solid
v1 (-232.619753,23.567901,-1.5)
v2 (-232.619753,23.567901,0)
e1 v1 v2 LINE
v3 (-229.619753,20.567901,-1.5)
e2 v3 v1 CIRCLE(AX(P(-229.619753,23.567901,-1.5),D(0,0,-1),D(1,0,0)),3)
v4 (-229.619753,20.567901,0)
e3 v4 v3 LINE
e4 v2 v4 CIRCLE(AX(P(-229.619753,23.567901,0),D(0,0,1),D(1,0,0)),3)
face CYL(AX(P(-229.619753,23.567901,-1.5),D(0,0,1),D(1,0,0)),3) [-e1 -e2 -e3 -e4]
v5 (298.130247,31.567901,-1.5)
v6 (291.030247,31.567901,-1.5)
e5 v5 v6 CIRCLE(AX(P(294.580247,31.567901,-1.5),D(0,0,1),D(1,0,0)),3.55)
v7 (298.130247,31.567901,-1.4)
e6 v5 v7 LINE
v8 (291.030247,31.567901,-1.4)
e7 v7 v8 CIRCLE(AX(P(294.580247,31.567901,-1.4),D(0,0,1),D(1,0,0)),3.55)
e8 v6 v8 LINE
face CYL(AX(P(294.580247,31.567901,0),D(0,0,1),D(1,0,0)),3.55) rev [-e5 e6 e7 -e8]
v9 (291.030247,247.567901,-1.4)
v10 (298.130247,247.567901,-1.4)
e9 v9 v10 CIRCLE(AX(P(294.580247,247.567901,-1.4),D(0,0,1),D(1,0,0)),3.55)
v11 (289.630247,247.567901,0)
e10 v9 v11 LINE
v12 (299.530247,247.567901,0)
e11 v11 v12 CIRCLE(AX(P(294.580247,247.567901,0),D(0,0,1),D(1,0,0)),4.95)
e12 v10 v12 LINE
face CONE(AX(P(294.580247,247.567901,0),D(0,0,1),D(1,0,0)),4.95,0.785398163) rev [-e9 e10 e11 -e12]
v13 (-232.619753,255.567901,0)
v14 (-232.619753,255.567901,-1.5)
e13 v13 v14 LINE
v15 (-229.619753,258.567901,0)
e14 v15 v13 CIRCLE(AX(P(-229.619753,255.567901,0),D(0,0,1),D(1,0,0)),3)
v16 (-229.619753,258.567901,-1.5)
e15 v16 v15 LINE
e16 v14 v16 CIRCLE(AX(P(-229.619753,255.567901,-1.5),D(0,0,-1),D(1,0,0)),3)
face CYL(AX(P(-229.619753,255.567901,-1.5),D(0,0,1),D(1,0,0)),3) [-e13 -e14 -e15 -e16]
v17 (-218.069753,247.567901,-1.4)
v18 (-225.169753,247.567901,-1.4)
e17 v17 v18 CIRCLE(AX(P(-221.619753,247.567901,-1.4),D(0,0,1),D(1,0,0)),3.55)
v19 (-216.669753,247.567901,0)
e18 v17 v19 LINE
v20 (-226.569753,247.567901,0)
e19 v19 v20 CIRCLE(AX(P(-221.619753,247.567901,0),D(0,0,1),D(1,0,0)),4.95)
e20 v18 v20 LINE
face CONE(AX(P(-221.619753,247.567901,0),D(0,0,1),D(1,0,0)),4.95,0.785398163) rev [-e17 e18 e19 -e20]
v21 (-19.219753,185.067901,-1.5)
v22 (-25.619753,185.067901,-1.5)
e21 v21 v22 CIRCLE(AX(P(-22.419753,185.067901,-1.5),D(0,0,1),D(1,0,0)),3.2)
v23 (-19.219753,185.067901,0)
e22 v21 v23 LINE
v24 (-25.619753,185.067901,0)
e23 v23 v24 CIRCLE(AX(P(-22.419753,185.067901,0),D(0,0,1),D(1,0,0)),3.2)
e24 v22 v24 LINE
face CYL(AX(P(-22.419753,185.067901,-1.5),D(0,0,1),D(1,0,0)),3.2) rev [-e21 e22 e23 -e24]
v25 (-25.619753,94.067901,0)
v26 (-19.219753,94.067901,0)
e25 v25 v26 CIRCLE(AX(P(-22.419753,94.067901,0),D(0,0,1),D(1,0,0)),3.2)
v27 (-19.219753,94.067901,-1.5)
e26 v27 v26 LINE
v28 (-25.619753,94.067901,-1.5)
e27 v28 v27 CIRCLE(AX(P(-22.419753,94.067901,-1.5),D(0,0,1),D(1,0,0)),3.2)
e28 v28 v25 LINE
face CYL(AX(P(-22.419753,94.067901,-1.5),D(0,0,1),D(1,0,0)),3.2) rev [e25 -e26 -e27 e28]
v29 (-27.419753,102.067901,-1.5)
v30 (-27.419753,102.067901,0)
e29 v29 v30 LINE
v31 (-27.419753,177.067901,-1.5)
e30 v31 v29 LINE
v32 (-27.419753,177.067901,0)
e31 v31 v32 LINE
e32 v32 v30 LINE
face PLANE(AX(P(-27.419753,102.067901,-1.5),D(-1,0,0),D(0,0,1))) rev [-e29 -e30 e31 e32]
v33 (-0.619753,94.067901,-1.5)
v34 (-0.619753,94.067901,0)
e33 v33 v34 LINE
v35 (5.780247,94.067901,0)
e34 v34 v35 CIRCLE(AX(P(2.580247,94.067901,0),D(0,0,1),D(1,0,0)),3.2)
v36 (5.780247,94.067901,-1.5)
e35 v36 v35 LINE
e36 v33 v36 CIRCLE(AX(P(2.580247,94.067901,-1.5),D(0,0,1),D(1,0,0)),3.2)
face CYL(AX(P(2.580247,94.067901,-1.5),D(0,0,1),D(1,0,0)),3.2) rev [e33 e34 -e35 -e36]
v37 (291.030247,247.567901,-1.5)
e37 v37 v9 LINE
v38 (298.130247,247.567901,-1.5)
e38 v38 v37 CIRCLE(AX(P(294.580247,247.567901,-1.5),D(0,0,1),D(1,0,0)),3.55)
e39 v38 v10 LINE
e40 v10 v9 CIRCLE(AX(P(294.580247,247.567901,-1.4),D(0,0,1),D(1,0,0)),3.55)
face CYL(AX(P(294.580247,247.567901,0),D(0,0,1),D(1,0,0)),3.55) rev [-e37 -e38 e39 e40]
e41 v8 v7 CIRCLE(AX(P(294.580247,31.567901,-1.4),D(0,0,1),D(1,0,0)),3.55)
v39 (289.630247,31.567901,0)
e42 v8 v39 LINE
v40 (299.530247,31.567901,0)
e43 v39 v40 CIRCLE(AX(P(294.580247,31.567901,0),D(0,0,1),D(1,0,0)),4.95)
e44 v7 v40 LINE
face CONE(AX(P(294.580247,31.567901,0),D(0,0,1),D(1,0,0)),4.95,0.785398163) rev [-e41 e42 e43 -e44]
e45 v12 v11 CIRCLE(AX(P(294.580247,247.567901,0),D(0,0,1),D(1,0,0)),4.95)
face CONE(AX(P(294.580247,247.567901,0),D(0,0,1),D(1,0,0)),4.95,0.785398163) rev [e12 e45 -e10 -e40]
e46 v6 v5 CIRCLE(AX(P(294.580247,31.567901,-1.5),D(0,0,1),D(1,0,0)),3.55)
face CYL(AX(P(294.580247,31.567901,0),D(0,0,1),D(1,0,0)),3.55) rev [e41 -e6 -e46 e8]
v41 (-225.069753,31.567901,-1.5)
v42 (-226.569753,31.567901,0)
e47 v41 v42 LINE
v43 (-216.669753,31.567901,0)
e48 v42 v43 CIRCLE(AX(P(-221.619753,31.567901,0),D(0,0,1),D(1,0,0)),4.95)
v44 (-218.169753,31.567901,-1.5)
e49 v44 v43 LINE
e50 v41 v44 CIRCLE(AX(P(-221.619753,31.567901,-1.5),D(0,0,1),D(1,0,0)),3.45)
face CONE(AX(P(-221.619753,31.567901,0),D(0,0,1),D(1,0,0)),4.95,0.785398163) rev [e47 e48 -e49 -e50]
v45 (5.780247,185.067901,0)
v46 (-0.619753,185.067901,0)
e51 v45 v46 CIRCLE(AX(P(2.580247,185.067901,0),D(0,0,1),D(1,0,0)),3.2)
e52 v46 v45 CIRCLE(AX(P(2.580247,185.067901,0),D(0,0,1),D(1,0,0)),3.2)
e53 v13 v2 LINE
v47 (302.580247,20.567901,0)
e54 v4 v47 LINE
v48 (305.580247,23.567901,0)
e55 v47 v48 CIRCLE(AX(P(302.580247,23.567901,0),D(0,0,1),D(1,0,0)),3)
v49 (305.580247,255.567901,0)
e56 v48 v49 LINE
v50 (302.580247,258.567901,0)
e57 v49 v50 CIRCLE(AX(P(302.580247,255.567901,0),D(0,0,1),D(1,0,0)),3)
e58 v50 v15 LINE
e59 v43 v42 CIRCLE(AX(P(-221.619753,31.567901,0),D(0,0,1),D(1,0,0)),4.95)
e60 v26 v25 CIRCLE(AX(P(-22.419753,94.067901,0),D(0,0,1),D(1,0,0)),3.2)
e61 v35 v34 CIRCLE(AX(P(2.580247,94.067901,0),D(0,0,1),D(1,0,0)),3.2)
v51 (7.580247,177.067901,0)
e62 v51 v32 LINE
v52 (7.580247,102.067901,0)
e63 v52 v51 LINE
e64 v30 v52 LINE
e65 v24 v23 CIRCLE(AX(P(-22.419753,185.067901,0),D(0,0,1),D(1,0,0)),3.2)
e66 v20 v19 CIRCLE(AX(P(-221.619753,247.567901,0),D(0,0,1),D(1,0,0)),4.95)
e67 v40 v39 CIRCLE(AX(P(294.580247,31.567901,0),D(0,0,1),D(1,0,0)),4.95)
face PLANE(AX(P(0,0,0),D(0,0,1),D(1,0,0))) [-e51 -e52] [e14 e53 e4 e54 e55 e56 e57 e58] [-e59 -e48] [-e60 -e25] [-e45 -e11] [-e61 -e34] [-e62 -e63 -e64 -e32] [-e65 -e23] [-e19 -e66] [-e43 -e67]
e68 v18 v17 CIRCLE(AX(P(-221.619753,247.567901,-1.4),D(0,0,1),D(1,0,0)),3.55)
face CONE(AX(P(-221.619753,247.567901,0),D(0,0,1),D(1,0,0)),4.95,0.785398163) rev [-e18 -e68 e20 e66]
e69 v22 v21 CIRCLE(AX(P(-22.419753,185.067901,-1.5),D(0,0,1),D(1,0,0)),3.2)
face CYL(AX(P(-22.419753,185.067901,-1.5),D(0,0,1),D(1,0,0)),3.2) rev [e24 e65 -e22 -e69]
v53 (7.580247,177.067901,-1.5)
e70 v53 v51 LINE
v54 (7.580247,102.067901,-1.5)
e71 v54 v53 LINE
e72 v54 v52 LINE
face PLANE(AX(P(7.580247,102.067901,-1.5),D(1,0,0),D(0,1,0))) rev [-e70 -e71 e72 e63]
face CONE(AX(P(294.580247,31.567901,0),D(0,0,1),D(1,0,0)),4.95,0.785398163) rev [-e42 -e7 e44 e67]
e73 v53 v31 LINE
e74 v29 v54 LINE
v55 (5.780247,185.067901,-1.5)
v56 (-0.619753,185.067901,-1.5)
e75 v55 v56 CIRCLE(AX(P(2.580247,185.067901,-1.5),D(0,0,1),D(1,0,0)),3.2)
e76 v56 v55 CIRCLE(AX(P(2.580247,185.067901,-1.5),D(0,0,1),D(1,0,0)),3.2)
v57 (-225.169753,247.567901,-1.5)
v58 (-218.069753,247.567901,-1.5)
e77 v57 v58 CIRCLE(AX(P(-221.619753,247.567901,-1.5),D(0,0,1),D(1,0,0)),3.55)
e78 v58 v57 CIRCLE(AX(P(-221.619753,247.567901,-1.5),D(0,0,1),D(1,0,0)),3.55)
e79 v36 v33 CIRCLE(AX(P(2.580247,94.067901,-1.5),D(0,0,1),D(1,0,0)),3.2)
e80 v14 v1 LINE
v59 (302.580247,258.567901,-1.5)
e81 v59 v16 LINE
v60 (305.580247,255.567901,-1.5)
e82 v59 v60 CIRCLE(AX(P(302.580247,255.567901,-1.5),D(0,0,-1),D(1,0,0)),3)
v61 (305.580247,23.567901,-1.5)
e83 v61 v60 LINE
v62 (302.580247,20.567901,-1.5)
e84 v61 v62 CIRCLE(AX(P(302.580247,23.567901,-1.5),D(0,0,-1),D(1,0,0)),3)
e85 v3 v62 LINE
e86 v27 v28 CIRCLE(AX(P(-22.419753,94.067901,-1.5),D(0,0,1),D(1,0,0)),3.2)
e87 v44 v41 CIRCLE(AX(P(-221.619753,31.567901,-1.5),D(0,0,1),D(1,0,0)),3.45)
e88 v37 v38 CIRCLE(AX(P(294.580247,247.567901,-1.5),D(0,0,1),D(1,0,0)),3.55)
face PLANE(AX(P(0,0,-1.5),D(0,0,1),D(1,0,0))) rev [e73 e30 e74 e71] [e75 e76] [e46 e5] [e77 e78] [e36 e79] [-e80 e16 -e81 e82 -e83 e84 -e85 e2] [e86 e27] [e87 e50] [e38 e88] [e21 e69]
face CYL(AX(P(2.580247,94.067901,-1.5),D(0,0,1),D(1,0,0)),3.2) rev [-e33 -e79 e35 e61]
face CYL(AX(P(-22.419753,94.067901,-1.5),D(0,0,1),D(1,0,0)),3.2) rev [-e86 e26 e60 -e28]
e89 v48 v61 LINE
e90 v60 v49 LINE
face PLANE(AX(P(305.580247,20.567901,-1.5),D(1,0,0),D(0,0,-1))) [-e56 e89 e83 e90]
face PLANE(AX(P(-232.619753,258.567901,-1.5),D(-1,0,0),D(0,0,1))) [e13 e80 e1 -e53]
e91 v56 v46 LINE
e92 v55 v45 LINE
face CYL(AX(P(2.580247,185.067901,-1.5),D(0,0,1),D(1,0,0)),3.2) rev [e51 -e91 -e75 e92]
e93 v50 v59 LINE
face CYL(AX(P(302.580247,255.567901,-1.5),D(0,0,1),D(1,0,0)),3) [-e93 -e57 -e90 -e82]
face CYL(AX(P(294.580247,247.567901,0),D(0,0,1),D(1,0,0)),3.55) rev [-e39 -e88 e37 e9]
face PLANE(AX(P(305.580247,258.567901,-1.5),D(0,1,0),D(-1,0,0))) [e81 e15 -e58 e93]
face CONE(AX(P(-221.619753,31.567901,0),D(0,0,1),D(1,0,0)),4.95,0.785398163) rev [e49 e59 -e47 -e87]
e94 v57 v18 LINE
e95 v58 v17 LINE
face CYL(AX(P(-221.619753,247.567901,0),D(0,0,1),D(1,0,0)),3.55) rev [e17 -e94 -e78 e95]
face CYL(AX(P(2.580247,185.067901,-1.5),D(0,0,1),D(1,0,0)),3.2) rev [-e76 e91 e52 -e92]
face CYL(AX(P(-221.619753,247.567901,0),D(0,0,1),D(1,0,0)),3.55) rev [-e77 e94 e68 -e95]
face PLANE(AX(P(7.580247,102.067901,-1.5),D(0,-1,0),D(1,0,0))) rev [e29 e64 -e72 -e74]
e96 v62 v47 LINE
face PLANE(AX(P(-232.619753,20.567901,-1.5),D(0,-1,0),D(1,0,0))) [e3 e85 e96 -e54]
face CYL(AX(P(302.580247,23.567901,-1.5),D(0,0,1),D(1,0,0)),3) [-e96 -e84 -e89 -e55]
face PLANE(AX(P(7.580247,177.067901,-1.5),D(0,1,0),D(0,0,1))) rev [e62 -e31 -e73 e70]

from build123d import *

# Parameters (mm, degrees)
SKETCH_1_W                       = 538.2
SKETCH_1_H                       = 238
EXTRUDE_1_DEPTH                  = 1.5
HOLE_WIZARD_7_1_7_1_1_AT_2_COUNT = 2
HOLE_WIZARD_7_1_7_1_1_AT_2_PITCH = 216
HOLE_WIZARD_7_1_7_1_1_AT_3_COUNT = 2
HOLE_WIZARD_7_1_7_1_1_AT_3_PITCH = 516.2
FILLET_1_R                       = 3
SKETCH_6_W                       = 35
SKETCH_6_H                       = 75
CUT_EXTRUDE_1_DEPTH              = 1.5
SKETCH_7_R                       = 3.2
CUT_EXTRUDE_2_DEPTH              = 1.5


with BuildPart() as part:
    # 草图1 → 凸台-拉伸1 (new body)
    with BuildSketch(Plane.XY):
        with Locations((36.480246914, 139.567901235)):
            Rectangle(SKETCH_1_W, SKETCH_1_H)
    extrude(amount=-EXTRUDE_1_DEPTH)

    # 草图2 → 孔1 (revolve, cut)
    with BuildSketch(Plane(origin=(-221.619753086, 31.567901235, 0), x_dir=(0, -1, 0), z_dir=(1, 0, 0))):
        Polygon((0, 0), (0, 1.5), (3.45, 1.5), (4.95, 0), align=None)
    revolve(axis=Axis((-221.619753086, 31.567901235, -110), (0, 0, 1)), mode=Mode.SUBTRACT)

    # 草图4 → Ø7.1 (7.1) 直径孔1 (revolve, cut)
    with BuildSketch(Plane(origin=(294.580246914, 247.567901235, 0), x_dir=(0, -1, 0), z_dir=(1, 0, 0))):
        Polygon((0, 0), (0, 1.5), (3.55, 1.5), (3.55, 1.4), (4.95, 0), align=None)
    hole_wizard_7_1_7_1_1 = revolve(axis=Axis((294.580246914, 247.567901235, 6.35), (0, 0, -1)), mode=Mode.SUBTRACT)

    # Ø7.1 (7.1) 直径孔1 at 2: Ø7.1 (7.1) 直径孔1 ×2
    with Locations(*[(0, -i * HOLE_WIZARD_7_1_7_1_1_AT_2_PITCH, 0) for i in range(1, HOLE_WIZARD_7_1_7_1_1_AT_2_COUNT)]):
        add(hole_wizard_7_1_7_1_1, mode=Mode.SUBTRACT)

    # Ø7.1 (7.1) 直径孔1 at 3: Ø7.1 (7.1) 直径孔1 ×2
    with Locations(*[(-i * HOLE_WIZARD_7_1_7_1_1_AT_3_PITCH, 0, 0) for i in range(1, HOLE_WIZARD_7_1_7_1_1_AT_3_COUNT)]):
        add(hole_wizard_7_1_7_1_1, mode=Mode.SUBTRACT)

    # 圆角1
    fillet_1_edges = [part.edges().sort_by_distance(p)[0] for p in [
        (-232.619753086, 258.567901235, -0.75),
        (305.580246914, 258.567901235, -0.75),
        (305.580246914, 20.567901235, -0.75),
        (-232.619753086, 20.567901235, -0.75),
    ]]
    fillet(fillet_1_edges, radius=FILLET_1_R)

    # 草图6 → 切除-拉伸1 (cut)
    with BuildSketch(Plane.XY):
        with Locations((-9.919753086, 139.567901235)):
            Rectangle(SKETCH_6_W, SKETCH_6_H)
    extrude(amount=-CUT_EXTRUDE_1_DEPTH, mode=Mode.SUBTRACT)

    # 草图7 → 切除-拉伸2 (cut)
    with BuildSketch(Plane.XY):
        with Locations((2.580246914, 94.067901235)):
            Circle(SKETCH_7_R)
        with Locations((-22.419753086, 94.067901235)):
            Circle(SKETCH_7_R)
        with Locations((2.580246914, 185.067901235)):
            Circle(SKETCH_7_R)
        with Locations((-22.419753086, 185.067901235)):
            Circle(SKETCH_7_R)
    extrude(amount=-CUT_EXTRUDE_2_DEPTH, mode=Mode.SUBTRACT)


solid = part.part
